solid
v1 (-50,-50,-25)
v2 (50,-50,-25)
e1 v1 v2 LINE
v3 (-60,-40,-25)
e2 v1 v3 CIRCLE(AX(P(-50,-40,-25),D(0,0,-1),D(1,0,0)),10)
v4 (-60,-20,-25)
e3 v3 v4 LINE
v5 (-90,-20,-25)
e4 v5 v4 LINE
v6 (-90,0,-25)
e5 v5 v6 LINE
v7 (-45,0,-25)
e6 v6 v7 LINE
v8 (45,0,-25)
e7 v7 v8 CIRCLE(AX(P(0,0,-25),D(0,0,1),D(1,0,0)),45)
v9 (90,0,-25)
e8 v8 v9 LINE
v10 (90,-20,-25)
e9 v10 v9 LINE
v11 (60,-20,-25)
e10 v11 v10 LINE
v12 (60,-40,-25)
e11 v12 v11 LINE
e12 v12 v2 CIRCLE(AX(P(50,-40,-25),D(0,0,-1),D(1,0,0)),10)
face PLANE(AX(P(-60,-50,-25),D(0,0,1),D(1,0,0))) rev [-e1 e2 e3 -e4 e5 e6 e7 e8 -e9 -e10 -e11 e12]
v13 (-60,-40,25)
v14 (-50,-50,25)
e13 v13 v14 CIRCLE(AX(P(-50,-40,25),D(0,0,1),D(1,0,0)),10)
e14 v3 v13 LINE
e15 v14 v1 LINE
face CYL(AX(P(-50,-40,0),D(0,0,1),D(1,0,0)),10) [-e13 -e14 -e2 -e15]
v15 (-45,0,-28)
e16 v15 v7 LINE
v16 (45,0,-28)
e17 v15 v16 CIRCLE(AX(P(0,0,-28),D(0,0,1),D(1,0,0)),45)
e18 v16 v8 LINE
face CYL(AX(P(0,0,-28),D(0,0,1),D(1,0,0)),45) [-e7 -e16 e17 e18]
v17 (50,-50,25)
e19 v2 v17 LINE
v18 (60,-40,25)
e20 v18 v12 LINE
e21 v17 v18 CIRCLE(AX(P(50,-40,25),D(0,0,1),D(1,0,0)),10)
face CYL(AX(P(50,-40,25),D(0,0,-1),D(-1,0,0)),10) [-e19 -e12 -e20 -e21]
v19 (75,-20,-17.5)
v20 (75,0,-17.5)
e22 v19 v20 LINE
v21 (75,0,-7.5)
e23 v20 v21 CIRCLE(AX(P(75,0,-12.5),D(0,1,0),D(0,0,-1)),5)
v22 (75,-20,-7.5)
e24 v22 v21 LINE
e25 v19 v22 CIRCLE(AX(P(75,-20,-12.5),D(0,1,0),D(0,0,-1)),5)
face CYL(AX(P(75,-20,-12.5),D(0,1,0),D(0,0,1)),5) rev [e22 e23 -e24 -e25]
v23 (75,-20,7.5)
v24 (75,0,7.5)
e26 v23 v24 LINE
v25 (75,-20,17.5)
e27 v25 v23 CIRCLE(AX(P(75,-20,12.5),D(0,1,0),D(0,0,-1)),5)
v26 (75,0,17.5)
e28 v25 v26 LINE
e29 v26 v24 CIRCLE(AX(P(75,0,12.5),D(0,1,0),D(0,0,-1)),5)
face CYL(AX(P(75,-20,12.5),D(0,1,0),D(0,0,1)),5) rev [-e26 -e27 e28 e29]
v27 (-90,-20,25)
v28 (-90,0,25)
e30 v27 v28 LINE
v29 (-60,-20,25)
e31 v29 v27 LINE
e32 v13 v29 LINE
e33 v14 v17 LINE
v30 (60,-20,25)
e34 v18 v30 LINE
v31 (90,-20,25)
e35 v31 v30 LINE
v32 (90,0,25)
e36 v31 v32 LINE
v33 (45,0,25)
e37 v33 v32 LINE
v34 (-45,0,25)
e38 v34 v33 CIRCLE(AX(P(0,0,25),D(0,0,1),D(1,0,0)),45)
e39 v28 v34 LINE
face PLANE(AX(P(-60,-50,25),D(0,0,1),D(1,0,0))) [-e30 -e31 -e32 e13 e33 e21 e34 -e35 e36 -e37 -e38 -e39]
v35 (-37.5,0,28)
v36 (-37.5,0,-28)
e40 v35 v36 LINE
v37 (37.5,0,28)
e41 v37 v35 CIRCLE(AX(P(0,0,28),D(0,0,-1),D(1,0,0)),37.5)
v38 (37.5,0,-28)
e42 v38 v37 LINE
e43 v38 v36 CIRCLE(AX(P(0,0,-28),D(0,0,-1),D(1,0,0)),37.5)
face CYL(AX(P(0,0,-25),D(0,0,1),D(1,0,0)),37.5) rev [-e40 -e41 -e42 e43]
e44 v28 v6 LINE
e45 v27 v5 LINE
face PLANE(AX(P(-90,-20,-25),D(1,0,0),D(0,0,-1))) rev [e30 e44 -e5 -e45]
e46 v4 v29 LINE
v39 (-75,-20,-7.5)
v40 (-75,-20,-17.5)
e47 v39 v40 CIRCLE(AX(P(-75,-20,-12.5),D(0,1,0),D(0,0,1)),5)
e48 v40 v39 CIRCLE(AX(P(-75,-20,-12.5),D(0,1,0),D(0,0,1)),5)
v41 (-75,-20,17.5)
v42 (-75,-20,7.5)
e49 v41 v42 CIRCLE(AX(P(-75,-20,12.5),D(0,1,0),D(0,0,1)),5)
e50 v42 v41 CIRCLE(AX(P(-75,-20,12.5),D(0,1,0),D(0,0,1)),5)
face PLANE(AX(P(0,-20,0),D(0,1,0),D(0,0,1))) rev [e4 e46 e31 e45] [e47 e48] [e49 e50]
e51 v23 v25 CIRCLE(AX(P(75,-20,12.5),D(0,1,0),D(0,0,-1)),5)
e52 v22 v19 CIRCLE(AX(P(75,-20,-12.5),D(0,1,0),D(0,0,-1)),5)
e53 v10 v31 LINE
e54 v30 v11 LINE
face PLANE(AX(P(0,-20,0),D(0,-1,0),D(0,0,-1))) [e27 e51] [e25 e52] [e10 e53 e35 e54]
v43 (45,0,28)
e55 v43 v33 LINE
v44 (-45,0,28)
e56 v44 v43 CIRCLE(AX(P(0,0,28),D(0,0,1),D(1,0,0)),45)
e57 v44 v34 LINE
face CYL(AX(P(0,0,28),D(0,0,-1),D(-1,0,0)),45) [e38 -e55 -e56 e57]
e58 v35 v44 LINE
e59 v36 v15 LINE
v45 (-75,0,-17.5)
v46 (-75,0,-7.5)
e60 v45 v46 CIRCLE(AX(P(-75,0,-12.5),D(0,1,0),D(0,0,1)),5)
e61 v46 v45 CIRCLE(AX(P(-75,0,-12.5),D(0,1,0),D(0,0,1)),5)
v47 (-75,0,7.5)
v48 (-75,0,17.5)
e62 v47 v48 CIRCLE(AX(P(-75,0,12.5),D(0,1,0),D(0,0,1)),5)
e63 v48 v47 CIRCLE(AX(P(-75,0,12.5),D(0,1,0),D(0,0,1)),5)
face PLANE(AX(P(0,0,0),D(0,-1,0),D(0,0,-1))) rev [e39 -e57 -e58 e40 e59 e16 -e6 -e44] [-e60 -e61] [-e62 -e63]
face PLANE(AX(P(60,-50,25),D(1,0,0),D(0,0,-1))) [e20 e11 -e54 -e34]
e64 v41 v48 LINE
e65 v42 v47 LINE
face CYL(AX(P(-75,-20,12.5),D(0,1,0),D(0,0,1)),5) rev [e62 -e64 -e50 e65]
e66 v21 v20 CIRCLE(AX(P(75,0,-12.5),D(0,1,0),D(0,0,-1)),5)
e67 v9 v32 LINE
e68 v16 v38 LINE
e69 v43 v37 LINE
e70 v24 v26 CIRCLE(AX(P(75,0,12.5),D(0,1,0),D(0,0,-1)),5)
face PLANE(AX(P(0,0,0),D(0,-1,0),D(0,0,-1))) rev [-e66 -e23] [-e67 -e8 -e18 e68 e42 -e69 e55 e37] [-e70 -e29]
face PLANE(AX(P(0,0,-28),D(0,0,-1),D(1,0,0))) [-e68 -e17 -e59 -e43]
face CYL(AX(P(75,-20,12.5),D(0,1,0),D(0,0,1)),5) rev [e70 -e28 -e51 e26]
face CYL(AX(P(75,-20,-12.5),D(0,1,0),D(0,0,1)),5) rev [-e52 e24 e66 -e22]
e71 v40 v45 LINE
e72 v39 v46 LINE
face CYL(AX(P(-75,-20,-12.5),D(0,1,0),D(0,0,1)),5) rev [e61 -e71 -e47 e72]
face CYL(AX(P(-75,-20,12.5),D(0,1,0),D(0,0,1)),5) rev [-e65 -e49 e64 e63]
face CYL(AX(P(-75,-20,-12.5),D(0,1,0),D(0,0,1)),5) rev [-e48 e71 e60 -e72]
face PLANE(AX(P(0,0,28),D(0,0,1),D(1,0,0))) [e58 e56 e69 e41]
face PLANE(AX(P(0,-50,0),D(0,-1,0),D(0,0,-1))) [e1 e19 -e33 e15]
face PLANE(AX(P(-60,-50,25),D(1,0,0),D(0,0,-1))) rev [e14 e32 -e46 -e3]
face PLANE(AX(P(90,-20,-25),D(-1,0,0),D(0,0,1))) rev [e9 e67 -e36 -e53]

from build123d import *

# Parameters (mm, degrees)
SKETCH_1_W          = 120
SKETCH_1_H          = 50
EXTRUDE_1_DEPTH     = 50
SKETCH_2_R          = 37.5
CUT_EXTRUDE_1_DEPTH = 50
SKETCH_3_W          = 30
SKETCH_3_H          = 50
EXTRUDE_3_DEPTH     = 20
FILLET_1_R          = 10
SKETCH_5_R          = 5
CUT_EXTRUDE_2_DEPTH = 20
EXTRUDE_START       = 3
EXTRUDE_4_DEPTH     = 3


with BuildPart() as part:
    # 草图1 → 凸台-拉伸1 (new body)
    with BuildSketch(Plane(origin=(0, 0, 0), x_dir=(1, 0, 0), z_dir=(0, 1, 0))):
        Rectangle(SKETCH_1_W, SKETCH_1_H)
    extrude(amount=-EXTRUDE_1_DEPTH)

    # 草图2 → 切除-拉伸1 (cut)
    with BuildSketch(Plane.XY.offset(25)):
        Circle(SKETCH_2_R)
    extrude(amount=-CUT_EXTRUDE_1_DEPTH, mode=Mode.SUBTRACT)

    # 草图3 → 凸台-拉伸3 (add)
    with BuildSketch(Plane.XZ):
        with Locations((-75, 0)):
            Rectangle(SKETCH_3_W, SKETCH_3_H)
        with Locations((75, 0)):
            Rectangle(SKETCH_3_W, SKETCH_3_H)
    extrude(amount=EXTRUDE_3_DEPTH)

    # 圆角1
    fillet_1_edges = [part.edges().sort_by_distance(p)[0] for p in [
        (60, -50, 0),
        (-60, -50, 0),
    ]]
    fillet(fillet_1_edges, radius=FILLET_1_R)

    # 草图5 → 切除-拉伸2 (cut)
    with BuildSketch(Plane(origin=(0, 0, 0), x_dir=(1, 0, 0), z_dir=(0, 1, 0))):
        with Locations(Location((-75, 12.5, 0), (0, 0, 270))):
            Circle(SKETCH_5_R)
        with Locations(Location((-75, -12.5, 0), (0, 0, 270))):
            Circle(SKETCH_5_R)
        with Locations(Location((75, -12.5, 0), (0, 0, 90))):
            Circle(SKETCH_5_R)
        with Locations(Location((75, 12.5, 0), (0, 0, 90))):
            Circle(SKETCH_5_R)
    extrude(amount=-CUT_EXTRUDE_2_DEPTH, mode=Mode.SUBTRACT)

    # 草图6 → 凸台-拉伸4 (add)
    with BuildSketch(Plane.XY.offset(25).offset(EXTRUDE_START)):
        with BuildLine():
            Line((-45, 0), (-37.5, 0))
            ThreePointArc((-37.5, 0), (0, -37.5), (37.5, 0))
            Line((37.5, 0), (45, 0))
            ThreePointArc((45, 0), (0, -45), (-45, 0))
        make_face()
    extrude_4 = extrude(amount=-EXTRUDE_4_DEPTH)

    # 镜向1: 凸台-拉伸4 across plane
    add(extrude_4.mirror(Plane.XY))


solid = part.part
